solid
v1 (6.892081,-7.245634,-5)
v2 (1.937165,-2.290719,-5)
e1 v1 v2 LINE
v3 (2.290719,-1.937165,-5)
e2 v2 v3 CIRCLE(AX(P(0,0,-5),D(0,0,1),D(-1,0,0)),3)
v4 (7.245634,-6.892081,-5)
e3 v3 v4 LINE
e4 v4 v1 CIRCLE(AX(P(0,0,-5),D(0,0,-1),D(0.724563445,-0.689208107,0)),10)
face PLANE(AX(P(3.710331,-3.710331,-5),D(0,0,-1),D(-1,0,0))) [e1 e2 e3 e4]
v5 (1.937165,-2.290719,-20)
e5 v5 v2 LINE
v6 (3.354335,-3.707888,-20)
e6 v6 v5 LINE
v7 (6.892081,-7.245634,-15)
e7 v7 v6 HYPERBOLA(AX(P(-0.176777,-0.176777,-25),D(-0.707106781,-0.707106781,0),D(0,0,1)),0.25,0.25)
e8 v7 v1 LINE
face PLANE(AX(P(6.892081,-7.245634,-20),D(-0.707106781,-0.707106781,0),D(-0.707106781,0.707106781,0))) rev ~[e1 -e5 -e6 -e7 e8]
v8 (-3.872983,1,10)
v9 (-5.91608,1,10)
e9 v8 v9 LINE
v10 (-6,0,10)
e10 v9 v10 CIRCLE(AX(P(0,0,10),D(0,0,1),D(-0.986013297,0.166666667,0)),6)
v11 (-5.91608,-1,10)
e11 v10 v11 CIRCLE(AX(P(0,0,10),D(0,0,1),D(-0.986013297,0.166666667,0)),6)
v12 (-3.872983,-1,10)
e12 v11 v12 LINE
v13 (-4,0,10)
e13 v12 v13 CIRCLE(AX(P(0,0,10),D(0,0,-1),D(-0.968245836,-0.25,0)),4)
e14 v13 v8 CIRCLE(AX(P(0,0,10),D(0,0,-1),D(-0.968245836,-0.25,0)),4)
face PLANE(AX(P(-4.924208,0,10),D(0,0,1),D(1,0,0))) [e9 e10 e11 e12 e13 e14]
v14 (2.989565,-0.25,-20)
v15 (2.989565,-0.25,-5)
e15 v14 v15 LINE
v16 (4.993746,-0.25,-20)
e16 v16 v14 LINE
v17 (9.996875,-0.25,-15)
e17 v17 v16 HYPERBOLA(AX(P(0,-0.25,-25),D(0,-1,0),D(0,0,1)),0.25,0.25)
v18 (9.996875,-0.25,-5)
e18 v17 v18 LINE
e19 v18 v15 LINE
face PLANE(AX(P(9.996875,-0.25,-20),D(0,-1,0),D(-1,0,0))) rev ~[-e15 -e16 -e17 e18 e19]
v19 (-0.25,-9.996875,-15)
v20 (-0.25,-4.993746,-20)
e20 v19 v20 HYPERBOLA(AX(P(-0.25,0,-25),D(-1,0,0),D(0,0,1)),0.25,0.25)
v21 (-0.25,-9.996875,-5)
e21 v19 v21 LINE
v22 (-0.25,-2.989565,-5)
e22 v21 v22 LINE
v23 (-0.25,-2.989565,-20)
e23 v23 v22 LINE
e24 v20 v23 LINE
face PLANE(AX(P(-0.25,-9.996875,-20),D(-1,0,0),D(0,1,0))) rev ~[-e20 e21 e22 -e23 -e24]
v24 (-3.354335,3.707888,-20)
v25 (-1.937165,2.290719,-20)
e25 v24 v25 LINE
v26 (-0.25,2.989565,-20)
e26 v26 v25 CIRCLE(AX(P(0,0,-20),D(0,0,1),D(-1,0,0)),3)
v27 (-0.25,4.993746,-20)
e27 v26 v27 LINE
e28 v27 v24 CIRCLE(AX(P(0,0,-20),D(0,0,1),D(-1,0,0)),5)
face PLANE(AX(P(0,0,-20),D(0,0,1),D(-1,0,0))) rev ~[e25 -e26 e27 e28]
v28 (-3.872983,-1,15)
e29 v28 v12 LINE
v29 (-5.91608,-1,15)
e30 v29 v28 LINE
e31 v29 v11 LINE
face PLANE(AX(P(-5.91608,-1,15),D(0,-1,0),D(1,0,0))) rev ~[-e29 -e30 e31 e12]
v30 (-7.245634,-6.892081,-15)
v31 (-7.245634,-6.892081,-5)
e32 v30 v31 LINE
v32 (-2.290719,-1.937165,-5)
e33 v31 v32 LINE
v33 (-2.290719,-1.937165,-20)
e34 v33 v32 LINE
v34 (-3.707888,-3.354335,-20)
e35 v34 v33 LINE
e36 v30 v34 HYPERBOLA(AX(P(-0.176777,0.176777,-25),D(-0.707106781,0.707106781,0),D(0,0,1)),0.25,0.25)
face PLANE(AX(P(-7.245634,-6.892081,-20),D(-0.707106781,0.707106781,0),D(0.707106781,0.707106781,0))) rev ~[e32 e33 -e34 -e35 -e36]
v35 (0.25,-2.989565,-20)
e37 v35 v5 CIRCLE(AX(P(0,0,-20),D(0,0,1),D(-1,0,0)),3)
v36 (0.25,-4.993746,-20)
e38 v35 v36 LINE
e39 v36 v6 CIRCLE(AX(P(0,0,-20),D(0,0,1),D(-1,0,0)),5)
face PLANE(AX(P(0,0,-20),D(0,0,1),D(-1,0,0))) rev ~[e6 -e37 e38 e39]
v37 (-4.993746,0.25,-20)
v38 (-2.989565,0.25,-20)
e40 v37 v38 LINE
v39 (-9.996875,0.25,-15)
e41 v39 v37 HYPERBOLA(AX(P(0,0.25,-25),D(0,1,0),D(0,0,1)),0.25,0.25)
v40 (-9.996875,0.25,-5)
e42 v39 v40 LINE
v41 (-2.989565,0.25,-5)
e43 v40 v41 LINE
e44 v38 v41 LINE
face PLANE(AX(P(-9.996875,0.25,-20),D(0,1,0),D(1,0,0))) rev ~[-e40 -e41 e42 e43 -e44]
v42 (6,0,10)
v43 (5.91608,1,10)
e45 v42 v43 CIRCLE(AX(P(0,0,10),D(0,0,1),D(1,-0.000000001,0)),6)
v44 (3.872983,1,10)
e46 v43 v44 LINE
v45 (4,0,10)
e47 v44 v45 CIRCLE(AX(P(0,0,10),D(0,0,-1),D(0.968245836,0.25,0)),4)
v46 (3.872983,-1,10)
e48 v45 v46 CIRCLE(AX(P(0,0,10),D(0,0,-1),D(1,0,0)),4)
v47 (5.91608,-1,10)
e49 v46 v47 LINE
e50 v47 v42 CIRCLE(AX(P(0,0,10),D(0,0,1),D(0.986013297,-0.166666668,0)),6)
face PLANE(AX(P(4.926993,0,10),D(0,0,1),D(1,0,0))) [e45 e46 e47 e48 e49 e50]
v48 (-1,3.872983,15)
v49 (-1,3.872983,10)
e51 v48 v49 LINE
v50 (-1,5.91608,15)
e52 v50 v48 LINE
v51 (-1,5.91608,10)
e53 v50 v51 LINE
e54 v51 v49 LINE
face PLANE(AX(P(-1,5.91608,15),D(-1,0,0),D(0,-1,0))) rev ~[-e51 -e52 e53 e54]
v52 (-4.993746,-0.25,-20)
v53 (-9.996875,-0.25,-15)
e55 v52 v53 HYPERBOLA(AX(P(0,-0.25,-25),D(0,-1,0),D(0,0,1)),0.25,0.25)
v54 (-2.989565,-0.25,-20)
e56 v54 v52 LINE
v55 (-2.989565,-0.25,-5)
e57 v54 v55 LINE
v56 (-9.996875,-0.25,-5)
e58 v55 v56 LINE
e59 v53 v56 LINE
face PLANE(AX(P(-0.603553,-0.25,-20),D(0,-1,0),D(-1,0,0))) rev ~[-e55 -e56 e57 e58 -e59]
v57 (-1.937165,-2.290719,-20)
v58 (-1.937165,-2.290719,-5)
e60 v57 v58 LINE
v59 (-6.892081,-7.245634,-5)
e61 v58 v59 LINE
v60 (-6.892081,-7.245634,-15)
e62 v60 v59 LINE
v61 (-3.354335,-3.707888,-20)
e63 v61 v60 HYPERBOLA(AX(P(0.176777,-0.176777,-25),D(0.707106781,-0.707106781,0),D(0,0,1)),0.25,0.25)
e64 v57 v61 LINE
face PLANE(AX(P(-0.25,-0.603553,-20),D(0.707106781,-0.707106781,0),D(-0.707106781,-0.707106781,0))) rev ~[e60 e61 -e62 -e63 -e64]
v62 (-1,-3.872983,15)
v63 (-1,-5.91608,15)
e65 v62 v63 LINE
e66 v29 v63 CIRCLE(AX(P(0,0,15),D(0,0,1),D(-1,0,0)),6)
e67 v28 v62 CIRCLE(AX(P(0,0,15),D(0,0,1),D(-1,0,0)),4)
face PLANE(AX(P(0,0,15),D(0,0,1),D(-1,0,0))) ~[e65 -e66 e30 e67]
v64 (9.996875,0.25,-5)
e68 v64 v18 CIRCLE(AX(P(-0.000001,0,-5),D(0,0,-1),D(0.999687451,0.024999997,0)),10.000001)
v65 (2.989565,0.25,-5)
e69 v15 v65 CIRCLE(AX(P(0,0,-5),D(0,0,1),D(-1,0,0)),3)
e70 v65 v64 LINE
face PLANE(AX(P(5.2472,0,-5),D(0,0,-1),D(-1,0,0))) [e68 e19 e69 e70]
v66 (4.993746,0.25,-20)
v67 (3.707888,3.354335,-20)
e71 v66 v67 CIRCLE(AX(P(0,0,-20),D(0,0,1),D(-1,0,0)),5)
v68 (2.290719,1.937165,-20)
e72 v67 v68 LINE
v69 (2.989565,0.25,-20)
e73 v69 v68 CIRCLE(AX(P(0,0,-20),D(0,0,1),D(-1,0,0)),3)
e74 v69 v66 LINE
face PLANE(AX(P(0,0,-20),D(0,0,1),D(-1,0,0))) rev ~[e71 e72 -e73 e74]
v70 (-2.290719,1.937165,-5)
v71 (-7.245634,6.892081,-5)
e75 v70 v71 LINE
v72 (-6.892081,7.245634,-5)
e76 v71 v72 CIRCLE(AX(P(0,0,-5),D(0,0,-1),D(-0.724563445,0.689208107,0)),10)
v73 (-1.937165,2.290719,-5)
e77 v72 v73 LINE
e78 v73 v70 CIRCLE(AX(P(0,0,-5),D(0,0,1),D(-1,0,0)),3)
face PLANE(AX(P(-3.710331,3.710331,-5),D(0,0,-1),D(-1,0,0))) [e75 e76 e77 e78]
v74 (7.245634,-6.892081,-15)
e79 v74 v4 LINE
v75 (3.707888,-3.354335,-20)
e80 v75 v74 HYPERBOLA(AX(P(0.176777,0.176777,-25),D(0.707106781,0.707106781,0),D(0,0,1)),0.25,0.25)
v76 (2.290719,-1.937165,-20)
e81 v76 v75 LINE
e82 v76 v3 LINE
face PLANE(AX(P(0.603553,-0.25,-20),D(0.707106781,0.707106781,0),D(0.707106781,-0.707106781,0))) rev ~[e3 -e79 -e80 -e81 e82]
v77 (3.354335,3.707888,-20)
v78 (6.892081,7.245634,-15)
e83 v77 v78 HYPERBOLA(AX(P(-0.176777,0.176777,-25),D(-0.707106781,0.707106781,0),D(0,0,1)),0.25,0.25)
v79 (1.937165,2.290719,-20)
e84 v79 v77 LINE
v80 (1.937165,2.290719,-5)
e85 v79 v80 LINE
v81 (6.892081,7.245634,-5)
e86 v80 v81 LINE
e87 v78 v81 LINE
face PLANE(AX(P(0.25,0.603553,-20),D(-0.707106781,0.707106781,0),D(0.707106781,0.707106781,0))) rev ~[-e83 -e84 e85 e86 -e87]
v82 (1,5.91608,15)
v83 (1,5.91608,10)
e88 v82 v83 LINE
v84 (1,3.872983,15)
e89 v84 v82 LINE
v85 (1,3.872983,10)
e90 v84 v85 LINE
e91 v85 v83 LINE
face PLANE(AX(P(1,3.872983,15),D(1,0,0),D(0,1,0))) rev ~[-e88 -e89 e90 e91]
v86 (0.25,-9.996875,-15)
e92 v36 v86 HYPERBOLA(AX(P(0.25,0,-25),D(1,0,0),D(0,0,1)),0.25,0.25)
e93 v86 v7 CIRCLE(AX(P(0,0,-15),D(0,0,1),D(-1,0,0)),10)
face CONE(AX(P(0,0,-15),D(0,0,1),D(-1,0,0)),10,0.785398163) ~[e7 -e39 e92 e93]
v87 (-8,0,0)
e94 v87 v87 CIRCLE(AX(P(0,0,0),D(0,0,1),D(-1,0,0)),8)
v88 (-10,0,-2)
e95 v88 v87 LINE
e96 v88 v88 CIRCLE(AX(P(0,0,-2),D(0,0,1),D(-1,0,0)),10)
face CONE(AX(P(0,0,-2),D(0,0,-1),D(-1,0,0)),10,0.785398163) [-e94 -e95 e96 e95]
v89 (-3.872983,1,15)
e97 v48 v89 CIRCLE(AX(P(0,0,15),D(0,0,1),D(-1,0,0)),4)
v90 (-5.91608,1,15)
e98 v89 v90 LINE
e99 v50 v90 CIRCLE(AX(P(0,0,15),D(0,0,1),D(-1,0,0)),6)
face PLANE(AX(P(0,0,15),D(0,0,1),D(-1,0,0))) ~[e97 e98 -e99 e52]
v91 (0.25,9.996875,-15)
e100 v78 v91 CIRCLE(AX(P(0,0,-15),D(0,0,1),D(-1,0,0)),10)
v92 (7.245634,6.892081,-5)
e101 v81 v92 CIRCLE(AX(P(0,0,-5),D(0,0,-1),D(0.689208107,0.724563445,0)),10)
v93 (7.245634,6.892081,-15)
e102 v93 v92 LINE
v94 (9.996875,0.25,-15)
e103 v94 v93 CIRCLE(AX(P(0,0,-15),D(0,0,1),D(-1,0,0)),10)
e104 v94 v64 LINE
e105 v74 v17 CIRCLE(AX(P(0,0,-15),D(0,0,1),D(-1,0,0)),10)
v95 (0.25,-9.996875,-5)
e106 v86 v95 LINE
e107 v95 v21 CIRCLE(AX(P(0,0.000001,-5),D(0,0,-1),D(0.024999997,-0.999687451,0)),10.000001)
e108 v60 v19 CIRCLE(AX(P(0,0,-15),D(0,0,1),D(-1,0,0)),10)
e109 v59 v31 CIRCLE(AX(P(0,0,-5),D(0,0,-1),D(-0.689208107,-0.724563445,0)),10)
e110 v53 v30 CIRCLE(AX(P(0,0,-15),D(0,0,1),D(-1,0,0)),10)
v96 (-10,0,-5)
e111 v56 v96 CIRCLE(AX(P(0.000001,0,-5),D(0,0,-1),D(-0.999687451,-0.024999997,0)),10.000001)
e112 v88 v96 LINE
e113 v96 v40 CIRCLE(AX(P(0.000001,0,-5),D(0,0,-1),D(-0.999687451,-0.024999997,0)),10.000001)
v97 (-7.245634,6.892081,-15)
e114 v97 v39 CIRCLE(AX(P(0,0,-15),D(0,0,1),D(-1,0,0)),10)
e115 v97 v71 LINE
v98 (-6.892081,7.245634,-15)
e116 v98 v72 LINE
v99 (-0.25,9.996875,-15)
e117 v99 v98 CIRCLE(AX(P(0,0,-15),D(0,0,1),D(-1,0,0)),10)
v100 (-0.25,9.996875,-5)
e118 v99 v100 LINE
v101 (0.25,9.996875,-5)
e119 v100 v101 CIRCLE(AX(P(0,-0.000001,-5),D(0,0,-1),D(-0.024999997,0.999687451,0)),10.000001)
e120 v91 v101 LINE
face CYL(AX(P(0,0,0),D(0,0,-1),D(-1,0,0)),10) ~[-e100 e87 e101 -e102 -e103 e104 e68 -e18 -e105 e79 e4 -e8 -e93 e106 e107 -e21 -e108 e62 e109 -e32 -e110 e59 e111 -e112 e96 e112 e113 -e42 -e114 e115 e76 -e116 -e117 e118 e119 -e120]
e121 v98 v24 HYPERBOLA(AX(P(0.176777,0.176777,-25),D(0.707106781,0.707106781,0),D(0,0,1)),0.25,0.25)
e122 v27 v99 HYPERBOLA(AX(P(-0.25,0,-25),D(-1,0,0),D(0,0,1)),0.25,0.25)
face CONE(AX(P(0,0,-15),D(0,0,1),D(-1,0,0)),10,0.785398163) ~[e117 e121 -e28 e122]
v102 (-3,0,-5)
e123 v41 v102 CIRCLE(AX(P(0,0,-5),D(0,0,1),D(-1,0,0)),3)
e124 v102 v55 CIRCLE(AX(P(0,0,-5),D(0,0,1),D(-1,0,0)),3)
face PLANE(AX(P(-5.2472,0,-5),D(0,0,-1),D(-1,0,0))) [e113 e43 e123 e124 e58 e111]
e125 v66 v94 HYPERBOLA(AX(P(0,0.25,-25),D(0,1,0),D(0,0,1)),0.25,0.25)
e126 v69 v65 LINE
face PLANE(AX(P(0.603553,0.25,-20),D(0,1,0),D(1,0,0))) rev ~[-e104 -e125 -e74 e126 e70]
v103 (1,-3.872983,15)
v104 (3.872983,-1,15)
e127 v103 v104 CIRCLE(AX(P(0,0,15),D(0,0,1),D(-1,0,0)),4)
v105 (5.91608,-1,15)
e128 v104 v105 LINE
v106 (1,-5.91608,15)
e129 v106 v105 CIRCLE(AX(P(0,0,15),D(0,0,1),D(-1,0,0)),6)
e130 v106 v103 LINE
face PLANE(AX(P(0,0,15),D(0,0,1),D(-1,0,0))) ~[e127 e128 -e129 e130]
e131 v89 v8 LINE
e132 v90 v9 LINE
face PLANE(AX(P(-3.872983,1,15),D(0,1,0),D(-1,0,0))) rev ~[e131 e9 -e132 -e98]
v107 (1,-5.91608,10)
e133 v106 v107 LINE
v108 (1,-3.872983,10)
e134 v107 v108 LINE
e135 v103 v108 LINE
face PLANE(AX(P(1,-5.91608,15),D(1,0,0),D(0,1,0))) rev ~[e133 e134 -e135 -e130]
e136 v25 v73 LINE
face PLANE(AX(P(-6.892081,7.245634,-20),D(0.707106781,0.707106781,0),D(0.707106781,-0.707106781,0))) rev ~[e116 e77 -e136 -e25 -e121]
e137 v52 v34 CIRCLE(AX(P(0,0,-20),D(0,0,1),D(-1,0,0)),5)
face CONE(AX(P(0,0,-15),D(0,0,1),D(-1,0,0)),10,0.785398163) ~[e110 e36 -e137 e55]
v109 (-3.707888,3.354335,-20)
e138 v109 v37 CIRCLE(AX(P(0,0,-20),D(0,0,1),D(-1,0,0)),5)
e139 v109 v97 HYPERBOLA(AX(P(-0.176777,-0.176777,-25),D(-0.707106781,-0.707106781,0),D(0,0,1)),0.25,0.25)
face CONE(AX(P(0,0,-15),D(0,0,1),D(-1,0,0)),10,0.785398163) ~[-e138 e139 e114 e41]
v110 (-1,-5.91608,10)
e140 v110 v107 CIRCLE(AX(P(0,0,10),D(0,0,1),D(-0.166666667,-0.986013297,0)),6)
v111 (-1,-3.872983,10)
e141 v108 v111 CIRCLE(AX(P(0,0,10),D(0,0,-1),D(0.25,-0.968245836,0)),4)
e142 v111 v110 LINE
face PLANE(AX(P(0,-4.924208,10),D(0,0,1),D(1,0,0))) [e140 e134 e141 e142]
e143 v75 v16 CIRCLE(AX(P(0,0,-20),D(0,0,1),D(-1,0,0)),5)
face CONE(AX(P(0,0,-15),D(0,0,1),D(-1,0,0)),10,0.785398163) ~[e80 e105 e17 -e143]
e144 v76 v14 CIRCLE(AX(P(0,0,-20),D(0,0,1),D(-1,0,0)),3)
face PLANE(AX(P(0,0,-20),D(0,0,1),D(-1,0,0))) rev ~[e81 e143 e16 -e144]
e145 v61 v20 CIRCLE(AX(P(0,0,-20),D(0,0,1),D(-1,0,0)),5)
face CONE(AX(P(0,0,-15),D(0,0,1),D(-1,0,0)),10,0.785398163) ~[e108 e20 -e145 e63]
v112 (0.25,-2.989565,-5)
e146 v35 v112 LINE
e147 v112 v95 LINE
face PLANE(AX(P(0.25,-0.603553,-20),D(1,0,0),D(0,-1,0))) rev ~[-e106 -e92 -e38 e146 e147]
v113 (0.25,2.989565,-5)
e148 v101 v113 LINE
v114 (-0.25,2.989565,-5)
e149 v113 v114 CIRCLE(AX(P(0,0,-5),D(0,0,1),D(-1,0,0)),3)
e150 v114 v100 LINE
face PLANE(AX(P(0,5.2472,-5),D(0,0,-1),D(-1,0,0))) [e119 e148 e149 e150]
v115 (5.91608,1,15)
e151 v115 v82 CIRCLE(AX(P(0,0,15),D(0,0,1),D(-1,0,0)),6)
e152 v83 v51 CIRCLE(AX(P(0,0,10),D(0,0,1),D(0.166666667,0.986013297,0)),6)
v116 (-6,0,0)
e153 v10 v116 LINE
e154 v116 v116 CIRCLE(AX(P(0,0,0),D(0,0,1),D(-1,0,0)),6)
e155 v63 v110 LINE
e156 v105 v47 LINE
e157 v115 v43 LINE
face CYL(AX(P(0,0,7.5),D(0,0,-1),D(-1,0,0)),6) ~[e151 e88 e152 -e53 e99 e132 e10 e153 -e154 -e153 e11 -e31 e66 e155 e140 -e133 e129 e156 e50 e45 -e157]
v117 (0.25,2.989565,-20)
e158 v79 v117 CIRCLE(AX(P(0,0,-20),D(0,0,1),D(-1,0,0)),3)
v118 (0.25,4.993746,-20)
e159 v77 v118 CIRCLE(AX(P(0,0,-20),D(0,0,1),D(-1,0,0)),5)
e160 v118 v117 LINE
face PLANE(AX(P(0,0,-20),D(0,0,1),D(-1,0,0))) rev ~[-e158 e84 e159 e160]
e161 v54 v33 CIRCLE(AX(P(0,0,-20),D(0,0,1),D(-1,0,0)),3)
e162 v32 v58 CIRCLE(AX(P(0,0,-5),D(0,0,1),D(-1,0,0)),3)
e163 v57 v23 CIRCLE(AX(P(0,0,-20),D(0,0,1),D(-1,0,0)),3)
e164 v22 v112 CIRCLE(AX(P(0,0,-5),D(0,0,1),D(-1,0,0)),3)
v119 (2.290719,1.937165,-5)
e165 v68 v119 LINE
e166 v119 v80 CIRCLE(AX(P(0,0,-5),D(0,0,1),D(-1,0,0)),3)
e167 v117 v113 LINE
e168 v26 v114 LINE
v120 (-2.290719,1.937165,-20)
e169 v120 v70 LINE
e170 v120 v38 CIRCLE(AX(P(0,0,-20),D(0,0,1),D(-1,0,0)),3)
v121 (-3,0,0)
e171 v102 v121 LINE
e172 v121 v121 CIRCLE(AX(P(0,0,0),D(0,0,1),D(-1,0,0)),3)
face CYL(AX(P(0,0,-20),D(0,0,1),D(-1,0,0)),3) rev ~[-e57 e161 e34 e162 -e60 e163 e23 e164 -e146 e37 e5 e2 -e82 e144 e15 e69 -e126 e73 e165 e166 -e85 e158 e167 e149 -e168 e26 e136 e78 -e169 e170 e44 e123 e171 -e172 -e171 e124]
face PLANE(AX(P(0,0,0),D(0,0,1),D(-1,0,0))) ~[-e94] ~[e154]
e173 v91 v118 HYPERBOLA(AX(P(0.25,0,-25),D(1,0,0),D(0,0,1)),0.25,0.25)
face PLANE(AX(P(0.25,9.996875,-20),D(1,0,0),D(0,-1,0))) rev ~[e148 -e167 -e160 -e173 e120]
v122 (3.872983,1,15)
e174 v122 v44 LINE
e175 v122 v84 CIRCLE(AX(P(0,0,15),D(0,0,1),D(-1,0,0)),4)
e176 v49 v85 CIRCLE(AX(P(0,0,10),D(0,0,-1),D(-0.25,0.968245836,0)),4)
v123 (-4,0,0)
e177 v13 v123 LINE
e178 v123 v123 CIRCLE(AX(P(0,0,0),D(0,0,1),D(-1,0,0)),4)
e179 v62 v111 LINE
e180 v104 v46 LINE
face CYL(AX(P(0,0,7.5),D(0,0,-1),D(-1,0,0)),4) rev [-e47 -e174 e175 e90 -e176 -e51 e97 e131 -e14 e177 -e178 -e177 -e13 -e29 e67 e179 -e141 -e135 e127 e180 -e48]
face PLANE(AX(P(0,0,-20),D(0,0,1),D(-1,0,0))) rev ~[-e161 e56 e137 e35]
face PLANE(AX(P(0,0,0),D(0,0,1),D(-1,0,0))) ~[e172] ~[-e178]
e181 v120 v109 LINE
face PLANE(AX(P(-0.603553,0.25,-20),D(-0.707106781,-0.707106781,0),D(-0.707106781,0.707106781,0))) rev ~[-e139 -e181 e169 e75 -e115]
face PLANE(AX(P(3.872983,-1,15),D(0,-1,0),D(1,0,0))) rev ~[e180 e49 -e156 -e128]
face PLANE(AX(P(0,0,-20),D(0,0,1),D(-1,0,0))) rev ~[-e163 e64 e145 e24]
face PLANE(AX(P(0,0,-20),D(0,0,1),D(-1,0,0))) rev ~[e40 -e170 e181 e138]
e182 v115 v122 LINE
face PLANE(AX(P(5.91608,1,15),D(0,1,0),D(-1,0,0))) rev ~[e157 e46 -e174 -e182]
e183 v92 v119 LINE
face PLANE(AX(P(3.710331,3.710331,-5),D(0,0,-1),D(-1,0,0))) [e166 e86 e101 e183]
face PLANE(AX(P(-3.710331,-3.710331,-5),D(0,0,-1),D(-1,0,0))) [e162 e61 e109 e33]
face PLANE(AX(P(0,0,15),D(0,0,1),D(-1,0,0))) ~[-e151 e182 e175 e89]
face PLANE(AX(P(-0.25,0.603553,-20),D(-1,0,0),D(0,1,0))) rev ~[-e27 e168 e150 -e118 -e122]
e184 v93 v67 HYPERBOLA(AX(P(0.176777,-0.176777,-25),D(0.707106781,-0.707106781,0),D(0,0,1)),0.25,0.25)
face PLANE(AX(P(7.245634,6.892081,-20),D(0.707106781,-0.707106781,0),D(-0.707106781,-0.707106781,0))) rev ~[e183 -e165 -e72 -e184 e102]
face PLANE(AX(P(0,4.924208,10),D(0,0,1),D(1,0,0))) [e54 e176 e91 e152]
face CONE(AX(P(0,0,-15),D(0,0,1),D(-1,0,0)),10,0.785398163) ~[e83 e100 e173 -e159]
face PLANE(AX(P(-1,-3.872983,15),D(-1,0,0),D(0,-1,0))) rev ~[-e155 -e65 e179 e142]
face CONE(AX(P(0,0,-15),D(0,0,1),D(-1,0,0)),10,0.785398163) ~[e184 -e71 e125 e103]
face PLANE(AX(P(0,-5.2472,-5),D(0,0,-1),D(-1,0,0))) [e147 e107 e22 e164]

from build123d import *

# Parameters (mm, degrees)
SKETCH1_W          = 2
SKETCH1_H          = 15
CUT_EXTRUDE1_DEPTH = 15
CHAMFER1_SIZE      = 2
CUT_EXTRUDE2_DEPTH = 5


with BuildPart() as part:
    # Sketch1 → Revolve1 (revolve)
    with BuildSketch(Plane(origin=(0, 0, 0), x_dir=(1, 0, 0), z_dir=(0, 1, 0)), mode=Mode.PRIVATE) as revolve1_sk:
        Polygon((3, 20), (3, 0), (4, 0), (6, 0), (10, 0), (10, 15), (5, 20), align=None)
        with Locations((5, -7.5)):
            Rectangle(SKETCH1_W, SKETCH1_H)
    revolve(revolve1_sk.sketch.rotate(Axis((0, 0, -20), (0, 0, 1)), 180), axis=Axis((0, 0, -20), (0, 0, 1)))

    # Sketch2 → Cut-Extrude1 (cut)
    with BuildSketch(Plane(origin=(0, 0, -20), x_dir=(-1, 0, 0), z_dir=(0, 0, -1))):
        with BuildLine():
            ThreePointArc((-9.996874512, 0.25), (-10, 0), (-9.996874512, -0.25))
            Line((-9.996874512, -0.25), (-0.603553391, -0.25))
            Line((-0.603553391, -0.25), (-0.353553391, 0))
            Line((-0.353553391, 0), (-0.603553391, 0.25))
            Line((-0.603553391, 0.25), (-9.996874512, 0.25))
        make_face()
        with BuildLine():
            Line((-0.25, -0.25), (-0.603553391, -0.25))
            Line((-0.603553391, -0.25), (-7.245634453, -6.892081063))
            ThreePointArc((-7.245634453, -6.892081063), (-7.071067812, -7.071067812), (-6.892081063, -7.245634453))
            Line((-6.892081063, -7.245634453), (-0.25, -0.603553391))
            Line((-0.25, -0.603553391), (-0.25, -0.25))
        make_face()
        with BuildLine():
            Line((-7.245634453, 6.892081063), (-0.603553391, 0.25))
            Line((-0.603553391, 0.25), (-0.25, 0.25))
            Line((-0.25, 0.25), (-0.25, 0.603553391))
            Line((-0.25, 0.603553391), (-6.892081063, 7.245634453))
            ThreePointArc((-6.892081063, 7.245634453), (-7.071067812, 7.071067812), (-7.245634453, 6.892081063))
        make_face()
        with BuildLine():
            Line((0, -0.353553391), (-0.25, -0.603553391))
            Line((-0.25, -0.603553391), (-0.25, -9.996874512))
            ThreePointArc((-0.25, -9.996874512), (0, -10), (0.25, -9.996874512))
            Line((0.25, -9.996874512), (0.25, -0.603553391))
            Line((0.25, -0.603553391), (0, -0.353553391))
        make_face()
        with BuildLine():
            Line((-0.25, 9.996874512), (-0.25, 0.603553391))
            Line((-0.25, 0.603553391), (0, 0.353553391))
            Line((0, 0.353553391), (0.25, 0.603553391))
            Line((0.25, 0.603553391), (0.25, 9.996874512))
            ThreePointArc((0.25, 9.996874512), (0, 10), (-0.25, 9.996874512))
        make_face()
        with BuildLine():
            Line((0.603553391, -0.25), (0.25, -0.25))
            Line((0.25, -0.25), (0.25, -0.603553391))
            Line((0.25, -0.603553391), (6.892081063, -7.245634453))
            ThreePointArc((6.892081063, -7.245634453), (7.071067812, -7.071067812), (7.245634453, -6.892081063))
            Line((7.245634453, -6.892081063), (0.603553391, -0.25))
        make_face()
        with BuildLine():
            Line((0.353553391, 0), (0.603553391, -0.25))
            Line((0.603553391, -0.25), (9.996874512, -0.25))
            ThreePointArc((9.996874512, -0.25), (10, 0), (9.996874512, 0.25))
            Line((9.996874512, 0.25), (0.603553391, 0.25))
            Line((0.603553391, 0.25), (0.353553391, 0))
        make_face()
        with BuildLine():
            Line((0.25, 0.603553391), (0.25, 0.25))
            Line((0.25, 0.25), (0.603553391, 0.25))
            Line((0.603553391, 0.25), (7.245634453, 6.892081063))
            ThreePointArc((7.245634453, 6.892081063), (7.071067812, 7.071067812), (6.892081063, 7.245634453))
            Line((6.892081063, 7.245634453), (0.25, 0.603553391))
        make_face()
    extrude(amount=-CUT_EXTRUDE1_DEPTH, mode=Mode.SUBTRACT)

    # Chamfer1
    chamfer1_edges = [part.edges().sort_by_distance(p)[0] for p in [
        (10, 0, 0),
    ]]
    chamfer(chamfer1_edges, length=CHAMFER1_SIZE)

    # Sketch3 → Cut-Extrude2 (cut)
    with BuildSketch(Plane.XY.offset(15)):
        with BuildLine():
            Line((1, 3.872983346), (1, 5.916079783))
            ThreePointArc((1, 5.916079783), (0, 6), (-1, 5.916079783))
            Line((-1, 5.916079783), (-1, 3.872983346))
            ThreePointArc((-1, 3.872983346), (0, 4), (1, 3.872983346))
        make_face()
        with BuildLine():
            ThreePointArc((6, 0), (5.978983137, 0.501757562), (5.916079783, 1))
            Line((5.916079783, 1), (3.872983346, 1))
            ThreePointArc((3.872983346, 1), (3.968118785, 0.50401717), (4, 0))
            ThreePointArc((4, 0), (3.968118785, -0.50401717), (3.872983346, -1))
            Line((3.872983346, -1), (5.916079783, -1))
            ThreePointArc((5.916079783, -1), (5.978983137, -0.501757562), (6, 0))
        make_face()
        with BuildLine():
            ThreePointArc((-1, -5.916079783), (0, -6), (1, -5.916079783))
            Line((1, -5.916079783), (1, -3.872983346))
            ThreePointArc((1, -3.872983346), (0, -4), (-1, -3.872983346))
            Line((-1, -3.872983346), (-1, -5.916079783))
        make_face()
        with BuildLine():
            Line((-3.872983346, 1), (-5.916079783, 1))
            ThreePointArc((-5.916079783, 1), (-6, 0), (-5.916079783, -1))
            Line((-5.916079783, -1), (-3.872983346, -1))
            ThreePointArc((-3.872983346, -1), (-4, 0), (-3.872983346, 1))
        make_face()
    extrude(amount=-CUT_EXTRUDE2_DEPTH, mode=Mode.SUBTRACT)


solid = part.part
